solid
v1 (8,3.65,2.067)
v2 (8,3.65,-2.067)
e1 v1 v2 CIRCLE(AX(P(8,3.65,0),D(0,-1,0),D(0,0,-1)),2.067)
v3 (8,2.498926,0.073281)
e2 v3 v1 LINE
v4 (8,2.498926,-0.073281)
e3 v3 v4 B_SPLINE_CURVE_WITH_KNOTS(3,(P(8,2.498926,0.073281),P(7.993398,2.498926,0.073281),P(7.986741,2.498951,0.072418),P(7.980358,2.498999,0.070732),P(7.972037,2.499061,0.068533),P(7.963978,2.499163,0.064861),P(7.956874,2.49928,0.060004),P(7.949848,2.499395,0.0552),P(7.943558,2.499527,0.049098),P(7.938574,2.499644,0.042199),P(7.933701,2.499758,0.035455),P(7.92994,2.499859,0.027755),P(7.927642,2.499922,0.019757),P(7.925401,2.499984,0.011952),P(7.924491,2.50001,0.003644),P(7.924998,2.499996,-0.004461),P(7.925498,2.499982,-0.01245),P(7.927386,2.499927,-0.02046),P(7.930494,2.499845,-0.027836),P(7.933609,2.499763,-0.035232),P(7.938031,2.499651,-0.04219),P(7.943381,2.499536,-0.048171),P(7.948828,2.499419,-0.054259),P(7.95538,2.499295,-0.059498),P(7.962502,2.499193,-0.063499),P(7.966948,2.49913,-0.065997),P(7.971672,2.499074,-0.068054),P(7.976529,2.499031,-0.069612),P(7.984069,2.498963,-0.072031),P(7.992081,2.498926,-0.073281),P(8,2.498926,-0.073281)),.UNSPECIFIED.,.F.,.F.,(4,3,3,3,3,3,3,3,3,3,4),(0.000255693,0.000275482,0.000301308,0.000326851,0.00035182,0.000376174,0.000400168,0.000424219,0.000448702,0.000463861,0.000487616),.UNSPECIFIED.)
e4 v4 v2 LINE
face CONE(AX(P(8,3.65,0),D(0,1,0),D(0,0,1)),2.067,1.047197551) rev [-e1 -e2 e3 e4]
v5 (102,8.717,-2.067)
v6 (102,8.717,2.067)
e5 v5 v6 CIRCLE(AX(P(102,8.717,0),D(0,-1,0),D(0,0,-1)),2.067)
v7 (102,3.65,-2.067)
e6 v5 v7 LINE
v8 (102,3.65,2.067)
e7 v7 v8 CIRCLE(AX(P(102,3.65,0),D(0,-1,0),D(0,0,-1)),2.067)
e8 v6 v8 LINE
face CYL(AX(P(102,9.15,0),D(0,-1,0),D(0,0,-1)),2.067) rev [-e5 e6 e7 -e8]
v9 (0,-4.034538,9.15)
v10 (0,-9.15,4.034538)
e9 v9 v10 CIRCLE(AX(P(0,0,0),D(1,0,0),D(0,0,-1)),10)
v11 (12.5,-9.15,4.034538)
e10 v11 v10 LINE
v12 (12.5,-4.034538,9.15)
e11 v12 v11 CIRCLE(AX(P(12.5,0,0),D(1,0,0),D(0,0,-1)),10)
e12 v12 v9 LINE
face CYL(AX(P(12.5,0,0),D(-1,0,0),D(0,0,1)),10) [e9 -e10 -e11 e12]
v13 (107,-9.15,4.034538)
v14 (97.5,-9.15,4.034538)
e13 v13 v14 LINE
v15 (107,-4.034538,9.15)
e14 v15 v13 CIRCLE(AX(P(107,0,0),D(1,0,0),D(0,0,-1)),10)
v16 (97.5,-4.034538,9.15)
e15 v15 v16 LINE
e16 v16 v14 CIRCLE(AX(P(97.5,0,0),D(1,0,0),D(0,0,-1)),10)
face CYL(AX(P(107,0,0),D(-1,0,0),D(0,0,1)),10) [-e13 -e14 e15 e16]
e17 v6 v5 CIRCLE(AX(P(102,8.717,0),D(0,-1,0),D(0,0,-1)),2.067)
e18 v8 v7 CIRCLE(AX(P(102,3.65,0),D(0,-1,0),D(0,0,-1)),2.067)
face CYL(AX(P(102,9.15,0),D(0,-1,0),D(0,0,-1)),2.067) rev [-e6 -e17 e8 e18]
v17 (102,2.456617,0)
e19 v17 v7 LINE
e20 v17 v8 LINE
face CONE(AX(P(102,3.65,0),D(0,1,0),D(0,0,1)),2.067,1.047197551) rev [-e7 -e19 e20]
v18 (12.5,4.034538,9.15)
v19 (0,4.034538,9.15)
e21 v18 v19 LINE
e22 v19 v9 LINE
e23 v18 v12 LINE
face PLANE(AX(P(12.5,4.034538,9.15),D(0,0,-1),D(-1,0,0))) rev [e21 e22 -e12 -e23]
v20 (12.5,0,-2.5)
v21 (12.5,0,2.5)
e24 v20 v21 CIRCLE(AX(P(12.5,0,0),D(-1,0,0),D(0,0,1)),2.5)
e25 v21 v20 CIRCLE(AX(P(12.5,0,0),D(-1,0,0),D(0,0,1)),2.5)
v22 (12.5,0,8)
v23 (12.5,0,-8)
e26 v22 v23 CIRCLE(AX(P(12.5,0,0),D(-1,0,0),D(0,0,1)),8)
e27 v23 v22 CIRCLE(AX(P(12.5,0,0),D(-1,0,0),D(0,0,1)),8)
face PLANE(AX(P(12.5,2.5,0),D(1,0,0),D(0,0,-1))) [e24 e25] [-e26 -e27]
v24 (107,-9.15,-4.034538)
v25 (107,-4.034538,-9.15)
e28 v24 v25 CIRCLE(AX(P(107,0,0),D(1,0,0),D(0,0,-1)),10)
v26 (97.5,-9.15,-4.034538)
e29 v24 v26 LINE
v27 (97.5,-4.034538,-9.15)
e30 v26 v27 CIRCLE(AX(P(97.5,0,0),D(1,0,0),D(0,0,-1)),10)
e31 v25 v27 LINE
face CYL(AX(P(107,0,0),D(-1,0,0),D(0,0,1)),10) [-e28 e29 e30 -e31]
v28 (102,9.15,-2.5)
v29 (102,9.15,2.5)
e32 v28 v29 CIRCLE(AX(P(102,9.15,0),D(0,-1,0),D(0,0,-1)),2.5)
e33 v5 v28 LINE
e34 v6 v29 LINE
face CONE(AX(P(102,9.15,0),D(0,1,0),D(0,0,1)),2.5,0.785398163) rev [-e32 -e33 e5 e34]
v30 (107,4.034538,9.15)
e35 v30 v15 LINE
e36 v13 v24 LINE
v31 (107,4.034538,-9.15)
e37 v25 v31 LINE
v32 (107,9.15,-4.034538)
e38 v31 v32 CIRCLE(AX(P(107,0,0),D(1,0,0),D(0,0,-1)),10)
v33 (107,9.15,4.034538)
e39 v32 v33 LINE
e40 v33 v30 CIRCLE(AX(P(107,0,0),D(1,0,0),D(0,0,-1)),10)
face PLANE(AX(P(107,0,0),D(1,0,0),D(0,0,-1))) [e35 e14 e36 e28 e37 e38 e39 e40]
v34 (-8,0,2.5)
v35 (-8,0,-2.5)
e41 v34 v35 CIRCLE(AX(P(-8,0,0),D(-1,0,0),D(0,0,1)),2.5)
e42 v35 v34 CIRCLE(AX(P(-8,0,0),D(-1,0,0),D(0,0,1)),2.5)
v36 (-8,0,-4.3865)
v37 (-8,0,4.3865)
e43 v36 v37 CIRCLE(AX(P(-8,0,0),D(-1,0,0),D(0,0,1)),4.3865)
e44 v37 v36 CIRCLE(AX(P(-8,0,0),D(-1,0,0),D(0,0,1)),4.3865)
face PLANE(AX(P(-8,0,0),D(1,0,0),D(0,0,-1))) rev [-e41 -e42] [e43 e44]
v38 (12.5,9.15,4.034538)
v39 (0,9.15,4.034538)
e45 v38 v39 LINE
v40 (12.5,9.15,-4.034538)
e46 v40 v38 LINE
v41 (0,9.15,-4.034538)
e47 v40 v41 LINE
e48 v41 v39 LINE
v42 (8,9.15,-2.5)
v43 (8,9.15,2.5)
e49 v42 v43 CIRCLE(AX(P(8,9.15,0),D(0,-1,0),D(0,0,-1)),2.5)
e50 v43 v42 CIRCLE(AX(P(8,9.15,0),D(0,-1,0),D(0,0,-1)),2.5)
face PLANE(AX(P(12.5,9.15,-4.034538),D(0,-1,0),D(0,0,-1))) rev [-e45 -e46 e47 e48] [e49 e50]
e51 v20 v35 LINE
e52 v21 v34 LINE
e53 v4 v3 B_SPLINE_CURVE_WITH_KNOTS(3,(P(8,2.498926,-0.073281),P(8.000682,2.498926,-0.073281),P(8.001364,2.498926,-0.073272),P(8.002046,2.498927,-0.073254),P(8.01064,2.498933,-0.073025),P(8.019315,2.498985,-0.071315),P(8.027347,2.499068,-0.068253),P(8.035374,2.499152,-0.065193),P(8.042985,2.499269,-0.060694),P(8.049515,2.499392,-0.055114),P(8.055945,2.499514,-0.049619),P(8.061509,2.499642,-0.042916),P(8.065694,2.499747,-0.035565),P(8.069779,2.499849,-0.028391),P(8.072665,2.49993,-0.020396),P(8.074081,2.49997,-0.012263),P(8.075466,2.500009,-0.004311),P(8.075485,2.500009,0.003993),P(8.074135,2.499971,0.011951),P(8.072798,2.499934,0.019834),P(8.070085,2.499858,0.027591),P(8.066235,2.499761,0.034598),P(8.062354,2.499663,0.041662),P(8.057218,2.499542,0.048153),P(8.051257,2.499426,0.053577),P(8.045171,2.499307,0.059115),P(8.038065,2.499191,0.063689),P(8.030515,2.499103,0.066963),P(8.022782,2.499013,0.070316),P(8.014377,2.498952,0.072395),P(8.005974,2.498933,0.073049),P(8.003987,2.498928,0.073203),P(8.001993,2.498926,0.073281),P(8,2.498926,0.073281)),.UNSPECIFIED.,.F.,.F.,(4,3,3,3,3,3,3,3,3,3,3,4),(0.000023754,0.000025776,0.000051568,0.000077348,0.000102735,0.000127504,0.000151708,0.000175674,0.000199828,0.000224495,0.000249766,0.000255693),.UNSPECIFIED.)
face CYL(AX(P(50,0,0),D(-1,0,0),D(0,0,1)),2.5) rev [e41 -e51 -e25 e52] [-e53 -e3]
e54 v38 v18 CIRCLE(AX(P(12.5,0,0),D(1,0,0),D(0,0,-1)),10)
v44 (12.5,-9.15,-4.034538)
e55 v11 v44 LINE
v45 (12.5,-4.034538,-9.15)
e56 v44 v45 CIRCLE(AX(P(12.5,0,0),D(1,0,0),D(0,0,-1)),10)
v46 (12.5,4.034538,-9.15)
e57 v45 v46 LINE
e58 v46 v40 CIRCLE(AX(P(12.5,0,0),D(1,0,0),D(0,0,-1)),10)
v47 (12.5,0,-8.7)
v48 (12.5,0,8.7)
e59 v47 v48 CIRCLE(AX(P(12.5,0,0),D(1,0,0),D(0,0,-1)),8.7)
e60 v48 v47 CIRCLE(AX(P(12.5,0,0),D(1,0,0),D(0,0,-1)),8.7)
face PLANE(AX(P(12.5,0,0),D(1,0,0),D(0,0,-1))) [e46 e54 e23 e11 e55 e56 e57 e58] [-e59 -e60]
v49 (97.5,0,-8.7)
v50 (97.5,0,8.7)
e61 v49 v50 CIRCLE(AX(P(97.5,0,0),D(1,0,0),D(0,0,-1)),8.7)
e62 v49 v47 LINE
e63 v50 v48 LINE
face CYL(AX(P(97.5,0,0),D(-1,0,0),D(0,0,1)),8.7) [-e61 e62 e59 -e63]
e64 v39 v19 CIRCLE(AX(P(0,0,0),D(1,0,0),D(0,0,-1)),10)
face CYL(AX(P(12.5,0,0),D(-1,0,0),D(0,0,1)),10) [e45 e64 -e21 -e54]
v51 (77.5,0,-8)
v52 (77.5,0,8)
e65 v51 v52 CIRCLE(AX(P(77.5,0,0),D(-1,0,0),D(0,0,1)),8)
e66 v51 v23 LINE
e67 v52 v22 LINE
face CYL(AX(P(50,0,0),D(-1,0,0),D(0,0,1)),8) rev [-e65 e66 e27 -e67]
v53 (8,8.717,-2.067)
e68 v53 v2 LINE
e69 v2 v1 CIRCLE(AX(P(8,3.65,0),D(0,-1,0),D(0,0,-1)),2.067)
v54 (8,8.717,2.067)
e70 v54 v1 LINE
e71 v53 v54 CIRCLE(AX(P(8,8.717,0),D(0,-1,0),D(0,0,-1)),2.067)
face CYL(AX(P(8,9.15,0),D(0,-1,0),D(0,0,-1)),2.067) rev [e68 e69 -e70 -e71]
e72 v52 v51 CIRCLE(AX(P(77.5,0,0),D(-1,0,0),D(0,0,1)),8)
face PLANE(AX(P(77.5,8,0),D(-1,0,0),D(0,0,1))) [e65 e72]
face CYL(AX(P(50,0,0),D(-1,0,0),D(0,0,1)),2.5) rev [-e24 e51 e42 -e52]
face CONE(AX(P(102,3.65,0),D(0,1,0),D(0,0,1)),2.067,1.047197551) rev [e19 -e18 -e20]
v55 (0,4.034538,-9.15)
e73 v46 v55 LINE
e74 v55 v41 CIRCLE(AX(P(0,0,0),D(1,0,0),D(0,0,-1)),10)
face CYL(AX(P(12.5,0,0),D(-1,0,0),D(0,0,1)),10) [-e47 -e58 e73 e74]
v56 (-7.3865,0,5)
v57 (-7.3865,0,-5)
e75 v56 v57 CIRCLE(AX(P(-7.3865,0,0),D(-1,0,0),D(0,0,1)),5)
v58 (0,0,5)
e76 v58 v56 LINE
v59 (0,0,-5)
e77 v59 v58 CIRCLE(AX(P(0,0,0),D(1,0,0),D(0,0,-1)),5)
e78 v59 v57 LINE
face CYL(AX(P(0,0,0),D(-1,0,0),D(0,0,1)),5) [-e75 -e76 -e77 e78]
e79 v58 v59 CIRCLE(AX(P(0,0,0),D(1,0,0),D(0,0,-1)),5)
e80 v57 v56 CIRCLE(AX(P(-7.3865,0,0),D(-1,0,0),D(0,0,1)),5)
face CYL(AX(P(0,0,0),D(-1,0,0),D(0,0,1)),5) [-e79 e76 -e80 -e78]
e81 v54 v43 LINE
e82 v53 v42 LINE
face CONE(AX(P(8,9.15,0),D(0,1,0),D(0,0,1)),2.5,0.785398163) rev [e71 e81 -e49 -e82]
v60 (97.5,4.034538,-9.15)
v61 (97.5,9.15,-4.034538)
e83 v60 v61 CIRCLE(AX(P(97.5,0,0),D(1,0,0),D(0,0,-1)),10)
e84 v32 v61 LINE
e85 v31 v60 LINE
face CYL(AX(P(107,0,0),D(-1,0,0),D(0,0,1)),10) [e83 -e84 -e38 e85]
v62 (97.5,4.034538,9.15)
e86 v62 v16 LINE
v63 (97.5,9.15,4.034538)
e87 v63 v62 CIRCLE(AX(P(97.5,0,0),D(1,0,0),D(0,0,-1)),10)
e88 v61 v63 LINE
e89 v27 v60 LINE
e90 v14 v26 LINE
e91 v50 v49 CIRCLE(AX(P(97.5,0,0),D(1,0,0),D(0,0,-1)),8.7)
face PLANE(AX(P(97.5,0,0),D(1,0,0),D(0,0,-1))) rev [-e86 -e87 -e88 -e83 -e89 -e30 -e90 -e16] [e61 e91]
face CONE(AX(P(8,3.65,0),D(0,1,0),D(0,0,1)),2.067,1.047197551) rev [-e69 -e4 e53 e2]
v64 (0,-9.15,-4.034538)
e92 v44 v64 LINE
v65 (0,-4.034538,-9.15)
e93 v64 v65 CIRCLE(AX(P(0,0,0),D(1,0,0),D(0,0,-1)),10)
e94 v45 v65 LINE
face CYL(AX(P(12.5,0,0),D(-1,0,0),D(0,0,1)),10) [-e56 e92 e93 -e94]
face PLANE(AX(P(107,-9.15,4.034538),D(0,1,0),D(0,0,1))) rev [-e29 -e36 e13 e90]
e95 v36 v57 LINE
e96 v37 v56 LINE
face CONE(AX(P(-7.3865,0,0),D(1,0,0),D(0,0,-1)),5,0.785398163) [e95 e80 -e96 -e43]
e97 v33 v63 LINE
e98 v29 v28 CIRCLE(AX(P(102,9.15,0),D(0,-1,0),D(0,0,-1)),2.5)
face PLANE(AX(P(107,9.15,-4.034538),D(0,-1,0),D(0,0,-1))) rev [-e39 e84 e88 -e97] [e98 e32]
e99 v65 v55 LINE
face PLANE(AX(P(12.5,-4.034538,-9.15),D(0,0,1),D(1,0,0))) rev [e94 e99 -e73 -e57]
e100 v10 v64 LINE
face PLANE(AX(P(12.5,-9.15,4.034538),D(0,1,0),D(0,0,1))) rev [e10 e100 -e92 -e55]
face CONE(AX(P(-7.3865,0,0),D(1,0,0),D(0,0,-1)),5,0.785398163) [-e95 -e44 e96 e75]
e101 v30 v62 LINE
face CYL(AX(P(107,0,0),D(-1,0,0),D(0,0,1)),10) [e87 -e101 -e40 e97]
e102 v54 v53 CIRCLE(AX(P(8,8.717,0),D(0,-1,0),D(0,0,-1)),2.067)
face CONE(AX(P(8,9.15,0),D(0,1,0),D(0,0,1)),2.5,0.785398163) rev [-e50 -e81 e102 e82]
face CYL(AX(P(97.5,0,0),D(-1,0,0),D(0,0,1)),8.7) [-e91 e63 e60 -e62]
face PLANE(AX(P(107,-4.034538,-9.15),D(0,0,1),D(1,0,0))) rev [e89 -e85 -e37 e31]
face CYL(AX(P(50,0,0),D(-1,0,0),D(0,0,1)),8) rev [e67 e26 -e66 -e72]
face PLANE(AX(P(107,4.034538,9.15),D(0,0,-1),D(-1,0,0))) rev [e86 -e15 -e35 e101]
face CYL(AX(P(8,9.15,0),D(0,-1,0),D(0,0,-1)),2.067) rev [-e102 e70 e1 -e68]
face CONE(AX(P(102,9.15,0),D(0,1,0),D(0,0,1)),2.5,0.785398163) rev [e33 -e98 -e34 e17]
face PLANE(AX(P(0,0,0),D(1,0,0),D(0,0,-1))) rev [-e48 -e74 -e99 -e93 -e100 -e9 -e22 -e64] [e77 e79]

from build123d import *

# Parameters (mm, degrees)
EXTRUDE_1_DEPTH = 12.5
SKETCH_3_R      = 8.7
EXTRUDE_2_DEPTH = 85
EXTRUDE_3_DEPTH = 9.5


with BuildPart() as part:
    # 草图1 → 旋转1 (revolve)
    with BuildSketch(Plane.XY, mode=Mode.PRIVATE) as revolve_1_sk:
        Polygon((-8, 0), (-8, 4.3865), (-7.3865, 5), (0, 5), (0, 0), align=None)
    revolve(revolve_1_sk.sketch.rotate(Axis((0, 0, 0), (-1, 0, 0)), 270), axis=Axis((0, 0, 0), (-1, 0, 0)))

    # 草图2 → 凸台-拉伸1 (add)
    with BuildSketch(Plane(origin=(0, 0, 0), x_dir=(0, 0, -1), z_dir=(1, 0, 0))):
        with BuildLine():
            Line((-4.034538387, -9.15), (4.034538387, -9.15))
            ThreePointArc((4.034538387, -9.15), (7.071067812, -7.071067812), (9.15, -4.034538387))
            Line((9.15, -4.034538387), (9.15, 4.034538387))
            ThreePointArc((9.15, 4.034538387), (7.071067812, 7.071067812), (4.034538387, 9.15))
            Line((4.034538387, 9.15), (-4.034538387, 9.15))
            ThreePointArc((-4.034538387, 9.15), (-7.071067812, 7.071067812), (-9.15, 4.034538387))
            Line((-9.15, 4.034538387), (-9.15, -4.034538387))
            ThreePointArc((-9.15, -4.034538387), (-7.071067812, -7.071067812), (-4.034538387, -9.15))
        make_face()
    extrude(amount=EXTRUDE_1_DEPTH)

    # 草图3 → 凸台-拉伸2 (add)
    with BuildSketch(Plane(origin=(12.5, 0, 0), x_dir=(0, 0, -1), z_dir=(1, 0, 0))):
        Circle(SKETCH_3_R)
    extrude(amount=EXTRUDE_2_DEPTH)

    # 草图4 → 凸台-拉伸3 (add)
    with BuildSketch(Plane(origin=(97.5, 0, 0), x_dir=(0, 0, -1), z_dir=(1, 0, 0))):
        with BuildLine():
            Line((-4.034538387, -9.15), (4.034538387, -9.15))
            ThreePointArc((4.034538387, -9.15), (7.071067812, -7.071067812), (9.15, -4.034538387))
            Line((9.15, -4.034538387), (9.15, 4.034538387))
            ThreePointArc((9.15, 4.034538387), (7.071067812, 7.071067812), (4.034538387, 9.15))
            Line((4.034538387, 9.15), (-4.034538387, 9.15))
            ThreePointArc((-4.034538387, 9.15), (-7.071067812, 7.071067812), (-9.15, 4.034538387))
            Line((-9.15, 4.034538387), (-9.15, -4.034538387))
            ThreePointArc((-9.15, -4.034538387), (-7.071067812, -7.071067812), (-4.034538387, -9.15))
        make_face()
    extrude(amount=EXTRUDE_3_DEPTH)

    # 草图5 → 切除-旋转1 (revolve, cut)
    with BuildSketch(Plane.XY, mode=Mode.PRIVATE) as cut_revolve_1_sk:
        Polygon((8, 2.456616994), (5.933, 3.65), (5.933, 8.717), (5.5, 9.15), (8, 9.15), align=None)
    revolve(cut_revolve_1_sk.sketch.rotate(Axis((8, 9.15, 0), (0, -1, 0)), 90), axis=Axis((8, 9.15, 0), (0, -1, 0)), mode=Mode.SUBTRACT)

    # 草图6 → 切除-旋转2 (revolve, cut)
    with BuildSketch(Plane.XY, mode=Mode.PRIVATE) as cut_revolve_2_sk:
        Polygon((102, 2.456616994), (99.933, 3.65), (99.933, 8.717), (99.5, 9.15), (102, 9.15), align=None)
    revolve(cut_revolve_2_sk.sketch.rotate(Axis((102, 9.15, 0), (0, -1, 0)), 90), axis=Axis((102, 9.15, 0), (0, -1, 0)), mode=Mode.SUBTRACT)

    # 草图7 → 切除-旋转3 (revolve, cut)
    with BuildSketch(Plane.XY, mode=Mode.PRIVATE) as cut_revolve_3_sk:
        Polygon((-8, 0), (-8, 2.5), (12.5, 2.5), (12.5, 8), (77.5, 8), (77.5, 0), align=None)
    revolve(cut_revolve_3_sk.sketch.rotate(Axis((50, 0, 0), (-1, 0, 0)), 270), axis=Axis((50, 0, 0), (-1, 0, 0)), mode=Mode.SUBTRACT)


solid = part.part
